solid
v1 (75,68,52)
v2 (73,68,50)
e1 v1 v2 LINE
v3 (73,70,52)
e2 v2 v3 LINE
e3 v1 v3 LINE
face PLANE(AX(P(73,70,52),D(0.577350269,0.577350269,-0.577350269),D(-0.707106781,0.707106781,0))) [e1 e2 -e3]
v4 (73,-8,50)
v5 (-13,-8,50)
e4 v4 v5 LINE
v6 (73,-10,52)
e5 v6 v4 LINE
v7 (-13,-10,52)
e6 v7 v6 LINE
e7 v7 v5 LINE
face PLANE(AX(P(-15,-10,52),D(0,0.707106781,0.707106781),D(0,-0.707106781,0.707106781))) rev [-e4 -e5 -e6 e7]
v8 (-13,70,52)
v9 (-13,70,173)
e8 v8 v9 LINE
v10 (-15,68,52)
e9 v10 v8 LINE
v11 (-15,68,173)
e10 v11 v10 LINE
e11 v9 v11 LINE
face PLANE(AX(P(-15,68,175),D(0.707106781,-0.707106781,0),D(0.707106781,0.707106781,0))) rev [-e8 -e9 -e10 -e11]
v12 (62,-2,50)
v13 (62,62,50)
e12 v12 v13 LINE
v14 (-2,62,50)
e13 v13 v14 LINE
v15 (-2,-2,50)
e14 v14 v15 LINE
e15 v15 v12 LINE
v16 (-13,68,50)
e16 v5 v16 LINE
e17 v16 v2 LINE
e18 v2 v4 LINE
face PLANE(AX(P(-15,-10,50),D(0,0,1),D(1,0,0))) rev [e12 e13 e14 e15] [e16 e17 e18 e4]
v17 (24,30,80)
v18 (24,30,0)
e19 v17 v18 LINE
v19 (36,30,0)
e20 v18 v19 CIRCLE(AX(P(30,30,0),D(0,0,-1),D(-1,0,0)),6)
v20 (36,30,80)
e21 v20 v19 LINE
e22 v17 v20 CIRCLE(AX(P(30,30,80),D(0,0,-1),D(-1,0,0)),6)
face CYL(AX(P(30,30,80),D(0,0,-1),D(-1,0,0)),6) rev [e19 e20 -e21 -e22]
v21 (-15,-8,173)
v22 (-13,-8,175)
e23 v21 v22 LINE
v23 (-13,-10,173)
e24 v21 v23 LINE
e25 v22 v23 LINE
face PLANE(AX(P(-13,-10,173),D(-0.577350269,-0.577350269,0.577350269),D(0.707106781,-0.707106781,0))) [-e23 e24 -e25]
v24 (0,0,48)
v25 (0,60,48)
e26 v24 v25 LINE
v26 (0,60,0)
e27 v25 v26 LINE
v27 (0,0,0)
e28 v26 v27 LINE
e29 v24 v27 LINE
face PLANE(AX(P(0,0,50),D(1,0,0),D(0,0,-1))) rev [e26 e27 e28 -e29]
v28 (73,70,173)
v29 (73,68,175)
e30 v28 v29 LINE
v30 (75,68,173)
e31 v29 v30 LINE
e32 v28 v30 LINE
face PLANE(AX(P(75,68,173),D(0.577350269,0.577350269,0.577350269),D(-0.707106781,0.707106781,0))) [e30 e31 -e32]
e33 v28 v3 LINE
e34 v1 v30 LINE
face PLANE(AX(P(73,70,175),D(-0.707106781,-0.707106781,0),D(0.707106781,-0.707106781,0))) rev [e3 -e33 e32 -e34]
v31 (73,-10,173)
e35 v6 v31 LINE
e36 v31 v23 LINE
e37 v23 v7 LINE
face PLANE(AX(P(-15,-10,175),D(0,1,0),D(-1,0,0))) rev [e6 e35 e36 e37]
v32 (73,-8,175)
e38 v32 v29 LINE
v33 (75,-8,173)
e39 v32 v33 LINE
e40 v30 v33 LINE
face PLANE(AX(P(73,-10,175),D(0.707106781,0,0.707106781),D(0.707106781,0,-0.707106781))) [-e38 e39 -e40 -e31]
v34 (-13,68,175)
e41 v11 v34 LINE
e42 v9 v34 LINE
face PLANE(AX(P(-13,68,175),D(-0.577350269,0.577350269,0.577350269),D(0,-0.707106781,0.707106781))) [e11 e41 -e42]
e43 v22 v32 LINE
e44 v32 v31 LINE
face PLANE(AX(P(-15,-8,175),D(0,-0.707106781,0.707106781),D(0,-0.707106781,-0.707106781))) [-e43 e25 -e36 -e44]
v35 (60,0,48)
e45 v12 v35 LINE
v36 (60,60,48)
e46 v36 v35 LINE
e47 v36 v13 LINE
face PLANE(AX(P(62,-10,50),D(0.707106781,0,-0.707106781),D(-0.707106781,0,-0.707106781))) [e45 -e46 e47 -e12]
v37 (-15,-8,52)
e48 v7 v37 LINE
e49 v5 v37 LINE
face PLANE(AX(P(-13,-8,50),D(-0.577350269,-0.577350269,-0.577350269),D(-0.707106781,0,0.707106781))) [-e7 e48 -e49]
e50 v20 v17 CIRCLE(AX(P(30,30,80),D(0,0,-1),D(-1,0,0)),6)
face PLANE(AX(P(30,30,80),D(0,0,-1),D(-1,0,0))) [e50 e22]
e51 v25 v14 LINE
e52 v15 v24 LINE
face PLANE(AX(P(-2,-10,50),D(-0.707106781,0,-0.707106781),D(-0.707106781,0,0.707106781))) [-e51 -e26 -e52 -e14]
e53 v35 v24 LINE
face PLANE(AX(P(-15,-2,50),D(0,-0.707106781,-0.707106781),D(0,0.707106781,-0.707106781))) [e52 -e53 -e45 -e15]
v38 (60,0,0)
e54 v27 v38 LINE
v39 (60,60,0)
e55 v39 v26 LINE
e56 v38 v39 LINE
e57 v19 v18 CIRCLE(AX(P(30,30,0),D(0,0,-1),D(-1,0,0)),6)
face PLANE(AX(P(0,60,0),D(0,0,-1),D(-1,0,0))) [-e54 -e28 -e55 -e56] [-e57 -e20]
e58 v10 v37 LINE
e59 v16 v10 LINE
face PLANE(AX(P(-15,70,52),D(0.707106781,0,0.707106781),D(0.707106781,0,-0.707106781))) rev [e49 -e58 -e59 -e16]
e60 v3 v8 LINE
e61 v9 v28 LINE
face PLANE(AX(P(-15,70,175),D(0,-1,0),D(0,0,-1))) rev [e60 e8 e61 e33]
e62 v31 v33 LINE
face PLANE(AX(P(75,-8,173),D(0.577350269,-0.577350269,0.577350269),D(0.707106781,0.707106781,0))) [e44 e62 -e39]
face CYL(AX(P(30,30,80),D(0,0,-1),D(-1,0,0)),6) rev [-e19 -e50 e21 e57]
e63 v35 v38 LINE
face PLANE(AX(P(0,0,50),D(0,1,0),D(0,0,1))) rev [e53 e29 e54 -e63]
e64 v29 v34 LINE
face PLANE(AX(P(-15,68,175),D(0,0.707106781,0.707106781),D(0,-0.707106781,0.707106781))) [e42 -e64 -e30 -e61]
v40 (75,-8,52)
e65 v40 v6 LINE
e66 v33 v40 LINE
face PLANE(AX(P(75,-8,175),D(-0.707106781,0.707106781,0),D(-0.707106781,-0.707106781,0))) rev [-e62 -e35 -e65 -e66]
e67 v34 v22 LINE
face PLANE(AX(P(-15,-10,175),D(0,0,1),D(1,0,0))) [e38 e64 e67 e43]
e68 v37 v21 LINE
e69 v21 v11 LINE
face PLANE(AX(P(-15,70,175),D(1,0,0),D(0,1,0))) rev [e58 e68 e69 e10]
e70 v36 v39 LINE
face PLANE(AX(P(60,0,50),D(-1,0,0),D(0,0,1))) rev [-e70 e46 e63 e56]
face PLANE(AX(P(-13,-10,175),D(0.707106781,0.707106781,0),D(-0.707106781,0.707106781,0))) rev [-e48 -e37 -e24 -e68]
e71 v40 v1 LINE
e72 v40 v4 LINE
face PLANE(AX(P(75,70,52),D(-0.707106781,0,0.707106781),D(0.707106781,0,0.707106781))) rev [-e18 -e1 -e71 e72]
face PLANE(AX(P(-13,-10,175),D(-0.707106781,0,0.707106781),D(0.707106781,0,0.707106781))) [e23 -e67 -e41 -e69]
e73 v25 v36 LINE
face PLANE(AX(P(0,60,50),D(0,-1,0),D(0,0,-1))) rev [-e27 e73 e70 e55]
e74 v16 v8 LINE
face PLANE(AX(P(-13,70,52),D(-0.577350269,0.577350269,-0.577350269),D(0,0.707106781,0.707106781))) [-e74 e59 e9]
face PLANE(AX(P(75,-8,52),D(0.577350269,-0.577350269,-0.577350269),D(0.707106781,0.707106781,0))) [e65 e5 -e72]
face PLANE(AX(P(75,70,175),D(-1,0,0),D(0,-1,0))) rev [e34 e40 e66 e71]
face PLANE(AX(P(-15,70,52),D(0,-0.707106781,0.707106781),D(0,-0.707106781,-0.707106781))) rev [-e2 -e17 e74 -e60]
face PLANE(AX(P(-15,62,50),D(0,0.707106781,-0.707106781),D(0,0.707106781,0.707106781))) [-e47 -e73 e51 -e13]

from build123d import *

# Parameters (mm, degrees)
SKETCH_1_W          = 60
SKETCH_1_H          = 60
EXTRUDE_227_DEPTH   = 50
SKETCH_2_W          = 90
SKETCH_2_H          = 80
EXTRUDE_1_DEPTH     = 125
CHAMFER_1_SIZE      = 2
SKETCH_3_R          = 6
CUT_EXTRUDE_1_DEPTH = 80


with BuildPart() as part:
    # 草图1 → Extrude 227 (new body)
    with BuildSketch(Plane.XY):
        with Locations((30, 30)):
            Rectangle(SKETCH_1_W, SKETCH_1_H)
    extrude(amount=EXTRUDE_227_DEPTH)

    # 草图2 → 凸台-拉伸1 (add)
    with BuildSketch(Plane.XY.offset(50)):
        with Locations((30, 30)):
            Rectangle(SKETCH_2_W, SKETCH_2_H)
    extrude(amount=EXTRUDE_1_DEPTH)

    # 倒角1
    chamfer_1_edges = [part.edges().sort_by_distance(p)[0] for p in [
        (-15, 70, 112.5),
        (75, 70, 112.5),
        (30, 70, 50),
        (30, 70, 175),
        (-15, -10, 112.5),
        (-15, 30, 50),
        (-15, 30, 175),
        (75, -10, 112.5),
        (75, 30, 50),
        (75, 30, 175),
        (30, -10, 50),
        (0, 30, 50),
        (30, 60, 50),
        (60, 30, 50),
        (30, 0, 50),
        (30, -10, 175),
    ]]
    chamfer(chamfer_1_edges, length=CHAMFER_1_SIZE)

    # 草图3 → 切除-拉伸1 (cut)
    with BuildSketch(Plane(origin=(0, 0, 0), x_dir=(-1, 0, 0), z_dir=(0, 0, -1))):
        with Locations((-30, 30)):
            Circle(SKETCH_3_R)
    extrude(amount=-CUT_EXTRUDE_1_DEPTH, mode=Mode.SUBTRACT)


solid = part.part
